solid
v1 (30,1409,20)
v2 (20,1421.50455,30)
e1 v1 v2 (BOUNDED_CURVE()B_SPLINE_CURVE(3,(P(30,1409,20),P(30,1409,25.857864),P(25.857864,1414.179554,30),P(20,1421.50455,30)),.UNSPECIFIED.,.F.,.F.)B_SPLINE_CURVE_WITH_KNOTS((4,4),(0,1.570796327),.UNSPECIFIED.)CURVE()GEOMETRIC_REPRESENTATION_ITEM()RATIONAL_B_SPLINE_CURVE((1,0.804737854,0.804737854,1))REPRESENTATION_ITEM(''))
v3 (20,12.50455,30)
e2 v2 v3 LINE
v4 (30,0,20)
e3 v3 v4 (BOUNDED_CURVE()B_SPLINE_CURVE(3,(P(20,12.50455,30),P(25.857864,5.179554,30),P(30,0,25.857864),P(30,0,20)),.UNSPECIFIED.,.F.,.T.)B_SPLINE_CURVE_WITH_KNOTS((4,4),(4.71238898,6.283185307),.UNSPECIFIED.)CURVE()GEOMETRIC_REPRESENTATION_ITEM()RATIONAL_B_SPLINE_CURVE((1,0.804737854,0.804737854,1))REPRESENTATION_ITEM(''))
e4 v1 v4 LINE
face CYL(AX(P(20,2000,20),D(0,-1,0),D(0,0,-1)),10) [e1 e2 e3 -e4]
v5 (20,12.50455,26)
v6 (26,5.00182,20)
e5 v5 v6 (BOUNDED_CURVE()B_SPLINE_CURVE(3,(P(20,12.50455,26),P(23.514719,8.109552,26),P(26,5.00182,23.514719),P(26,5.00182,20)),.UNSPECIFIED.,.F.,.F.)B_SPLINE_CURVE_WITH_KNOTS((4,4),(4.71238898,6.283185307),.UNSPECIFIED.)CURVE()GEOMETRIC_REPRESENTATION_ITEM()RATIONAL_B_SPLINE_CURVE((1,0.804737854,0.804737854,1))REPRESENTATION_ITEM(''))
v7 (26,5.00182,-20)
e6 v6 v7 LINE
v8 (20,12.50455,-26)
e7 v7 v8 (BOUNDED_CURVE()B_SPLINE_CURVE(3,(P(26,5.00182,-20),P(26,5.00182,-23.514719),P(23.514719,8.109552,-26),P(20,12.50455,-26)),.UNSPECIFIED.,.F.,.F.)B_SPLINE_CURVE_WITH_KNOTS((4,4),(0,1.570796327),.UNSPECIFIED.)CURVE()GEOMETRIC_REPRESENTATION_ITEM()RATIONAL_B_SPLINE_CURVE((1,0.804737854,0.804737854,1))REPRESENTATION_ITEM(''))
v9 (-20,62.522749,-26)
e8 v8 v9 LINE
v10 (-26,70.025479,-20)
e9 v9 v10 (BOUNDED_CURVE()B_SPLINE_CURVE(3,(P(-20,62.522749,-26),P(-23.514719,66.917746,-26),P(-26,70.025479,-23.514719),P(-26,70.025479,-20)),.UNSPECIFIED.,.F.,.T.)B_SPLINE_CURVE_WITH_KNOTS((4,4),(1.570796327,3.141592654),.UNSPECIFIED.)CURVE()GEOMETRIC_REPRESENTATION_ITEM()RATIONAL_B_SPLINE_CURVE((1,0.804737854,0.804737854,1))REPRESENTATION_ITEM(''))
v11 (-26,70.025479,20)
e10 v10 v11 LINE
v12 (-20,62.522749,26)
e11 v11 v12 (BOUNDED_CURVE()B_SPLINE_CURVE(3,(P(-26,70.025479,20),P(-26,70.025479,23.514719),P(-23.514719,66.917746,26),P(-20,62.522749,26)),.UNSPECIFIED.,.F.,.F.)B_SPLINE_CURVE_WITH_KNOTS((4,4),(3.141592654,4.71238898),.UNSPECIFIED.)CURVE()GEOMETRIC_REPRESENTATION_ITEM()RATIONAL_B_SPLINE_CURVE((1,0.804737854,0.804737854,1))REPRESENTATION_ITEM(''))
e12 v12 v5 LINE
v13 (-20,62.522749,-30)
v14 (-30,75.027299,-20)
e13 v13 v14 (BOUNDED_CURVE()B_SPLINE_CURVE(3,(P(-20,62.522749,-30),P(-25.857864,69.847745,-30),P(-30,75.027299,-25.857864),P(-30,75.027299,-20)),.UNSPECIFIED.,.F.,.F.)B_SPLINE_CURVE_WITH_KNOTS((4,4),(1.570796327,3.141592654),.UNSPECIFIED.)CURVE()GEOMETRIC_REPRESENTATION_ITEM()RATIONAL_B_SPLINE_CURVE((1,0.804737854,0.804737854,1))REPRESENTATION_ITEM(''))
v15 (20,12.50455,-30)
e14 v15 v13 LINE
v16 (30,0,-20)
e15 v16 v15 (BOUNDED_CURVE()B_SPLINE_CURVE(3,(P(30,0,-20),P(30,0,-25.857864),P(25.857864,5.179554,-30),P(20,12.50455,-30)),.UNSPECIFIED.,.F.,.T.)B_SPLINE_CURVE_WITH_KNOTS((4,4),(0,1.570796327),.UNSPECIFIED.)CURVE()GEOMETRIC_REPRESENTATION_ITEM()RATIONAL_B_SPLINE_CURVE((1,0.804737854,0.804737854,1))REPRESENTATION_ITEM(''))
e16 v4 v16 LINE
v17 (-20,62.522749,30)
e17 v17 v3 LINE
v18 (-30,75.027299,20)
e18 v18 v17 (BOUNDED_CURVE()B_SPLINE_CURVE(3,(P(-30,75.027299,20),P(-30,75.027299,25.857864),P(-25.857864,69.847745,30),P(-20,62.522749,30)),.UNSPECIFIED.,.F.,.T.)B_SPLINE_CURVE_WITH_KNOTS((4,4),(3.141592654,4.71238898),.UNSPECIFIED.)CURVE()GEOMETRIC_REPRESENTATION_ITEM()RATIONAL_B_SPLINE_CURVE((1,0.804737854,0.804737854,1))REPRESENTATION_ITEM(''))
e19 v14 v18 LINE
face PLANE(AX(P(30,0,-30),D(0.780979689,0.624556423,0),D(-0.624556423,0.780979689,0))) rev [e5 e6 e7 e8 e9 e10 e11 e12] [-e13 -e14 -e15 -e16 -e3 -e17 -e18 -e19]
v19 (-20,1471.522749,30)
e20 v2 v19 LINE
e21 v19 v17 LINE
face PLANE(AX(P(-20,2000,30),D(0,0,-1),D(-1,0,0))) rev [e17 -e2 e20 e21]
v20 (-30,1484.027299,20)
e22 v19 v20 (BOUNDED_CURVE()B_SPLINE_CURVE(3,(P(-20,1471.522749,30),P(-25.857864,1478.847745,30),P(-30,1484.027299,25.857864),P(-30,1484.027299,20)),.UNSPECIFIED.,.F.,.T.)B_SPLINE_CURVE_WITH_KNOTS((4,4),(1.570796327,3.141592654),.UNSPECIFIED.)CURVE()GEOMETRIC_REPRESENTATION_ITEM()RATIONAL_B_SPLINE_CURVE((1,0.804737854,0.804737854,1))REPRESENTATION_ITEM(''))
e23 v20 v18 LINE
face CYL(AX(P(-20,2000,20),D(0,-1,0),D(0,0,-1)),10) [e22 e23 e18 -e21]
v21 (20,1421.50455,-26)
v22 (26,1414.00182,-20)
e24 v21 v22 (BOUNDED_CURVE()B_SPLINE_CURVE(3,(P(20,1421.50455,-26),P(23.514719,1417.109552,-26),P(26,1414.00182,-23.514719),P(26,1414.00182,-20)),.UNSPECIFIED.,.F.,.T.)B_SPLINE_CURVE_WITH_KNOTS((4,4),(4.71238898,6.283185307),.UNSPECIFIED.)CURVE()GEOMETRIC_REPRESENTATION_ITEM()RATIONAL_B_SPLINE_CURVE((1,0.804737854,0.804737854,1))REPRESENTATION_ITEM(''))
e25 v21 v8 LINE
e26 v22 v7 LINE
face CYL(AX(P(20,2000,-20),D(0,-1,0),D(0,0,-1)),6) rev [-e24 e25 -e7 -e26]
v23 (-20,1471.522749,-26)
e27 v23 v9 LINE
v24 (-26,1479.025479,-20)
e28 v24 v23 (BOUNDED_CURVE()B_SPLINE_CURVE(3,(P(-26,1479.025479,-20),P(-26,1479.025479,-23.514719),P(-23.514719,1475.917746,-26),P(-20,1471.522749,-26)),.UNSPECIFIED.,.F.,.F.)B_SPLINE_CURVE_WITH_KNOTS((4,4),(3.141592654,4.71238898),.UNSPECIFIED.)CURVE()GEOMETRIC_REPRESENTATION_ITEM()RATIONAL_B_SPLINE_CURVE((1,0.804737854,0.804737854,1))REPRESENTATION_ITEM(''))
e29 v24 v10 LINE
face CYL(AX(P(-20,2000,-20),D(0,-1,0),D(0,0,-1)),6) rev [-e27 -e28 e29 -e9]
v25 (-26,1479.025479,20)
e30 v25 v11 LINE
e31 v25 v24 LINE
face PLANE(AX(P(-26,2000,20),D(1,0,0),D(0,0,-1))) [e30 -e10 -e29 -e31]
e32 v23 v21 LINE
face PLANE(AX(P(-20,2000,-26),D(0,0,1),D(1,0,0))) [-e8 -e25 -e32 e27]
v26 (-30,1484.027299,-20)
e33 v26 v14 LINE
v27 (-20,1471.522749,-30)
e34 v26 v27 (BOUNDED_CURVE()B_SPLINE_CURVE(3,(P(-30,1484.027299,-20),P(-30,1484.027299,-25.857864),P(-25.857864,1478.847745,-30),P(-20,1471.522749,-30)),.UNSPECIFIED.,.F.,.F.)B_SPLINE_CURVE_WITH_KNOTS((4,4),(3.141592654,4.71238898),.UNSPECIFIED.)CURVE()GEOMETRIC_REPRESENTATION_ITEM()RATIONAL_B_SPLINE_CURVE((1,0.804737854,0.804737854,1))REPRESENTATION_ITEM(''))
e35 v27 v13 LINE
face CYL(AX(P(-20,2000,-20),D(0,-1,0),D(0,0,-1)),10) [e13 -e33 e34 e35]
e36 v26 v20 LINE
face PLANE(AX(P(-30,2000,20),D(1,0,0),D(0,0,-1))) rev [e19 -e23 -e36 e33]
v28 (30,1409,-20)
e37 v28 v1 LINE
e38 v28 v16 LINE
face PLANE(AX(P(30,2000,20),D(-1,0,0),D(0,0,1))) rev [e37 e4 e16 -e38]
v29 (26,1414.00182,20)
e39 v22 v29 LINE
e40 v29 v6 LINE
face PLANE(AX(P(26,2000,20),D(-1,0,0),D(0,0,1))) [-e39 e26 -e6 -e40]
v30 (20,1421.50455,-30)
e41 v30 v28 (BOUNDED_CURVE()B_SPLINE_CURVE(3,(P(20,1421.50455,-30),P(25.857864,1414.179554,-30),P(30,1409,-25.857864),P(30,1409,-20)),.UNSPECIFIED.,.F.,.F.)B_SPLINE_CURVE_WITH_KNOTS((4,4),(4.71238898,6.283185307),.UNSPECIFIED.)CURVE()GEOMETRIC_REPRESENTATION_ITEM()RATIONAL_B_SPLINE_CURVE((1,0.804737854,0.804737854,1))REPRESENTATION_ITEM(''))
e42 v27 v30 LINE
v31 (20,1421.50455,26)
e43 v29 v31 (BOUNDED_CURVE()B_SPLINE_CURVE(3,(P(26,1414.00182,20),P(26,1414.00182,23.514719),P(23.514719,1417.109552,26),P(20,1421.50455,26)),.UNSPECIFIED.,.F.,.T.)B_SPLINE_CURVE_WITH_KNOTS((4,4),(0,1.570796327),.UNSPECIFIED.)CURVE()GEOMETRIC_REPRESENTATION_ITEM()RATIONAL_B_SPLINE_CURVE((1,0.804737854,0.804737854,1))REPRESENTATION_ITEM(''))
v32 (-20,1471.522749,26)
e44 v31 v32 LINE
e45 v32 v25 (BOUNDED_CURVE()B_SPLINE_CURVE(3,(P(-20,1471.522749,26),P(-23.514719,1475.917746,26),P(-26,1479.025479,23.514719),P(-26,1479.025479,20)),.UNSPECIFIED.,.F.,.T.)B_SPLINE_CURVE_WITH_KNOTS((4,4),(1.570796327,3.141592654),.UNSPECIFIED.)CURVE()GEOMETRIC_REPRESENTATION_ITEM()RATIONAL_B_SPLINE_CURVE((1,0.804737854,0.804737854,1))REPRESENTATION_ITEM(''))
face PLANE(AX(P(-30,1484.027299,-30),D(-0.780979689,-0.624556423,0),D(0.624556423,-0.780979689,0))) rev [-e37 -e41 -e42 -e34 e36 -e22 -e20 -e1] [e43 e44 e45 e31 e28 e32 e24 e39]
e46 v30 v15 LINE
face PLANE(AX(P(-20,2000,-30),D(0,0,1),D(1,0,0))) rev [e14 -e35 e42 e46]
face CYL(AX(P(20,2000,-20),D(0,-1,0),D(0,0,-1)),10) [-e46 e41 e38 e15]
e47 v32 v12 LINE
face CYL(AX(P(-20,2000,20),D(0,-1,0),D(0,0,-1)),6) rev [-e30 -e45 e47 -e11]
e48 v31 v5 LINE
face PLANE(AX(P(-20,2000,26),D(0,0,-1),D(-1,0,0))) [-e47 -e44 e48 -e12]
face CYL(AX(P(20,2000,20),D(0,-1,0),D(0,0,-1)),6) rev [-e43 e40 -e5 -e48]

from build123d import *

# Parameters (mm, degrees)
BOSS_EXTRUDE1_DEPTH     = 2000
CUT_EXTRUDE1_DEPTH      = 2002.124683772
CUT_EXTRUDE1_DEPTH_BACK = 2002.124683772


with BuildPart() as part:
    # Sketch1 → Boss-Extrude1 (new body)
    with BuildSketch(Plane(origin=(0, 0, 0), x_dir=(1, 0, 0), z_dir=(0, 1, 0))):
        with BuildLine():
            Line((-20, -30), (20, -30))
            ThreePointArc((20, -30), (27.071067812, -27.071067812), (30, -20))
            Line((30, -20), (30, 20))
            ThreePointArc((30, 20), (27.071067812, 27.071067812), (20, 30))
            Line((20, 30), (-20, 30))
            ThreePointArc((-20, 30), (-27.071067812, 27.071067812), (-30, 20))
            Line((-30, 20), (-30, -20))
            ThreePointArc((-30, -20), (-27.071067812, -27.071067812), (-20, -30))
        make_face()
        with BuildLine():
            Line((-26, -20), (-26, 20))
            ThreePointArc((-26, 20), (-24.242640687, 24.242640687), (-20, 26))
            Line((-20, 26), (20, 26))
            ThreePointArc((20, 26), (24.242640687, 24.242640687), (26, 20))
            Line((26, 20), (26, -20))
            ThreePointArc((26, -20), (24.242640687, -24.242640687), (20, -26))
            Line((20, -26), (-20, -26))
            ThreePointArc((-20, -26), (-24.242640687, -24.242640687), (-26, -20))
        make_face(mode=Mode.SUBTRACT)
    extrude(amount=BOSS_EXTRUDE1_DEPTH)

    # Sketch2 → Cut-Extrude1 (cut, two sides: drawn at the far end of the back side and taken through both)
    with BuildSketch(Plane.XY.offset(30).offset(-CUT_EXTRUDE1_DEPTH_BACK)):
        Polygon((30, 0), (-30, 75.027298751), (-170.24369385, -210.007574385), align=None)
        Polygon((-30, 1484.027298751), (30, 1409), (525.992052796, 1638.556238223), (8.977575366, 2080.626411119), (-421.015295507, 1818.362615914), align=None)
    extrude(amount=CUT_EXTRUDE1_DEPTH + CUT_EXTRUDE1_DEPTH_BACK, mode=Mode.SUBTRACT)


solid = part.part
